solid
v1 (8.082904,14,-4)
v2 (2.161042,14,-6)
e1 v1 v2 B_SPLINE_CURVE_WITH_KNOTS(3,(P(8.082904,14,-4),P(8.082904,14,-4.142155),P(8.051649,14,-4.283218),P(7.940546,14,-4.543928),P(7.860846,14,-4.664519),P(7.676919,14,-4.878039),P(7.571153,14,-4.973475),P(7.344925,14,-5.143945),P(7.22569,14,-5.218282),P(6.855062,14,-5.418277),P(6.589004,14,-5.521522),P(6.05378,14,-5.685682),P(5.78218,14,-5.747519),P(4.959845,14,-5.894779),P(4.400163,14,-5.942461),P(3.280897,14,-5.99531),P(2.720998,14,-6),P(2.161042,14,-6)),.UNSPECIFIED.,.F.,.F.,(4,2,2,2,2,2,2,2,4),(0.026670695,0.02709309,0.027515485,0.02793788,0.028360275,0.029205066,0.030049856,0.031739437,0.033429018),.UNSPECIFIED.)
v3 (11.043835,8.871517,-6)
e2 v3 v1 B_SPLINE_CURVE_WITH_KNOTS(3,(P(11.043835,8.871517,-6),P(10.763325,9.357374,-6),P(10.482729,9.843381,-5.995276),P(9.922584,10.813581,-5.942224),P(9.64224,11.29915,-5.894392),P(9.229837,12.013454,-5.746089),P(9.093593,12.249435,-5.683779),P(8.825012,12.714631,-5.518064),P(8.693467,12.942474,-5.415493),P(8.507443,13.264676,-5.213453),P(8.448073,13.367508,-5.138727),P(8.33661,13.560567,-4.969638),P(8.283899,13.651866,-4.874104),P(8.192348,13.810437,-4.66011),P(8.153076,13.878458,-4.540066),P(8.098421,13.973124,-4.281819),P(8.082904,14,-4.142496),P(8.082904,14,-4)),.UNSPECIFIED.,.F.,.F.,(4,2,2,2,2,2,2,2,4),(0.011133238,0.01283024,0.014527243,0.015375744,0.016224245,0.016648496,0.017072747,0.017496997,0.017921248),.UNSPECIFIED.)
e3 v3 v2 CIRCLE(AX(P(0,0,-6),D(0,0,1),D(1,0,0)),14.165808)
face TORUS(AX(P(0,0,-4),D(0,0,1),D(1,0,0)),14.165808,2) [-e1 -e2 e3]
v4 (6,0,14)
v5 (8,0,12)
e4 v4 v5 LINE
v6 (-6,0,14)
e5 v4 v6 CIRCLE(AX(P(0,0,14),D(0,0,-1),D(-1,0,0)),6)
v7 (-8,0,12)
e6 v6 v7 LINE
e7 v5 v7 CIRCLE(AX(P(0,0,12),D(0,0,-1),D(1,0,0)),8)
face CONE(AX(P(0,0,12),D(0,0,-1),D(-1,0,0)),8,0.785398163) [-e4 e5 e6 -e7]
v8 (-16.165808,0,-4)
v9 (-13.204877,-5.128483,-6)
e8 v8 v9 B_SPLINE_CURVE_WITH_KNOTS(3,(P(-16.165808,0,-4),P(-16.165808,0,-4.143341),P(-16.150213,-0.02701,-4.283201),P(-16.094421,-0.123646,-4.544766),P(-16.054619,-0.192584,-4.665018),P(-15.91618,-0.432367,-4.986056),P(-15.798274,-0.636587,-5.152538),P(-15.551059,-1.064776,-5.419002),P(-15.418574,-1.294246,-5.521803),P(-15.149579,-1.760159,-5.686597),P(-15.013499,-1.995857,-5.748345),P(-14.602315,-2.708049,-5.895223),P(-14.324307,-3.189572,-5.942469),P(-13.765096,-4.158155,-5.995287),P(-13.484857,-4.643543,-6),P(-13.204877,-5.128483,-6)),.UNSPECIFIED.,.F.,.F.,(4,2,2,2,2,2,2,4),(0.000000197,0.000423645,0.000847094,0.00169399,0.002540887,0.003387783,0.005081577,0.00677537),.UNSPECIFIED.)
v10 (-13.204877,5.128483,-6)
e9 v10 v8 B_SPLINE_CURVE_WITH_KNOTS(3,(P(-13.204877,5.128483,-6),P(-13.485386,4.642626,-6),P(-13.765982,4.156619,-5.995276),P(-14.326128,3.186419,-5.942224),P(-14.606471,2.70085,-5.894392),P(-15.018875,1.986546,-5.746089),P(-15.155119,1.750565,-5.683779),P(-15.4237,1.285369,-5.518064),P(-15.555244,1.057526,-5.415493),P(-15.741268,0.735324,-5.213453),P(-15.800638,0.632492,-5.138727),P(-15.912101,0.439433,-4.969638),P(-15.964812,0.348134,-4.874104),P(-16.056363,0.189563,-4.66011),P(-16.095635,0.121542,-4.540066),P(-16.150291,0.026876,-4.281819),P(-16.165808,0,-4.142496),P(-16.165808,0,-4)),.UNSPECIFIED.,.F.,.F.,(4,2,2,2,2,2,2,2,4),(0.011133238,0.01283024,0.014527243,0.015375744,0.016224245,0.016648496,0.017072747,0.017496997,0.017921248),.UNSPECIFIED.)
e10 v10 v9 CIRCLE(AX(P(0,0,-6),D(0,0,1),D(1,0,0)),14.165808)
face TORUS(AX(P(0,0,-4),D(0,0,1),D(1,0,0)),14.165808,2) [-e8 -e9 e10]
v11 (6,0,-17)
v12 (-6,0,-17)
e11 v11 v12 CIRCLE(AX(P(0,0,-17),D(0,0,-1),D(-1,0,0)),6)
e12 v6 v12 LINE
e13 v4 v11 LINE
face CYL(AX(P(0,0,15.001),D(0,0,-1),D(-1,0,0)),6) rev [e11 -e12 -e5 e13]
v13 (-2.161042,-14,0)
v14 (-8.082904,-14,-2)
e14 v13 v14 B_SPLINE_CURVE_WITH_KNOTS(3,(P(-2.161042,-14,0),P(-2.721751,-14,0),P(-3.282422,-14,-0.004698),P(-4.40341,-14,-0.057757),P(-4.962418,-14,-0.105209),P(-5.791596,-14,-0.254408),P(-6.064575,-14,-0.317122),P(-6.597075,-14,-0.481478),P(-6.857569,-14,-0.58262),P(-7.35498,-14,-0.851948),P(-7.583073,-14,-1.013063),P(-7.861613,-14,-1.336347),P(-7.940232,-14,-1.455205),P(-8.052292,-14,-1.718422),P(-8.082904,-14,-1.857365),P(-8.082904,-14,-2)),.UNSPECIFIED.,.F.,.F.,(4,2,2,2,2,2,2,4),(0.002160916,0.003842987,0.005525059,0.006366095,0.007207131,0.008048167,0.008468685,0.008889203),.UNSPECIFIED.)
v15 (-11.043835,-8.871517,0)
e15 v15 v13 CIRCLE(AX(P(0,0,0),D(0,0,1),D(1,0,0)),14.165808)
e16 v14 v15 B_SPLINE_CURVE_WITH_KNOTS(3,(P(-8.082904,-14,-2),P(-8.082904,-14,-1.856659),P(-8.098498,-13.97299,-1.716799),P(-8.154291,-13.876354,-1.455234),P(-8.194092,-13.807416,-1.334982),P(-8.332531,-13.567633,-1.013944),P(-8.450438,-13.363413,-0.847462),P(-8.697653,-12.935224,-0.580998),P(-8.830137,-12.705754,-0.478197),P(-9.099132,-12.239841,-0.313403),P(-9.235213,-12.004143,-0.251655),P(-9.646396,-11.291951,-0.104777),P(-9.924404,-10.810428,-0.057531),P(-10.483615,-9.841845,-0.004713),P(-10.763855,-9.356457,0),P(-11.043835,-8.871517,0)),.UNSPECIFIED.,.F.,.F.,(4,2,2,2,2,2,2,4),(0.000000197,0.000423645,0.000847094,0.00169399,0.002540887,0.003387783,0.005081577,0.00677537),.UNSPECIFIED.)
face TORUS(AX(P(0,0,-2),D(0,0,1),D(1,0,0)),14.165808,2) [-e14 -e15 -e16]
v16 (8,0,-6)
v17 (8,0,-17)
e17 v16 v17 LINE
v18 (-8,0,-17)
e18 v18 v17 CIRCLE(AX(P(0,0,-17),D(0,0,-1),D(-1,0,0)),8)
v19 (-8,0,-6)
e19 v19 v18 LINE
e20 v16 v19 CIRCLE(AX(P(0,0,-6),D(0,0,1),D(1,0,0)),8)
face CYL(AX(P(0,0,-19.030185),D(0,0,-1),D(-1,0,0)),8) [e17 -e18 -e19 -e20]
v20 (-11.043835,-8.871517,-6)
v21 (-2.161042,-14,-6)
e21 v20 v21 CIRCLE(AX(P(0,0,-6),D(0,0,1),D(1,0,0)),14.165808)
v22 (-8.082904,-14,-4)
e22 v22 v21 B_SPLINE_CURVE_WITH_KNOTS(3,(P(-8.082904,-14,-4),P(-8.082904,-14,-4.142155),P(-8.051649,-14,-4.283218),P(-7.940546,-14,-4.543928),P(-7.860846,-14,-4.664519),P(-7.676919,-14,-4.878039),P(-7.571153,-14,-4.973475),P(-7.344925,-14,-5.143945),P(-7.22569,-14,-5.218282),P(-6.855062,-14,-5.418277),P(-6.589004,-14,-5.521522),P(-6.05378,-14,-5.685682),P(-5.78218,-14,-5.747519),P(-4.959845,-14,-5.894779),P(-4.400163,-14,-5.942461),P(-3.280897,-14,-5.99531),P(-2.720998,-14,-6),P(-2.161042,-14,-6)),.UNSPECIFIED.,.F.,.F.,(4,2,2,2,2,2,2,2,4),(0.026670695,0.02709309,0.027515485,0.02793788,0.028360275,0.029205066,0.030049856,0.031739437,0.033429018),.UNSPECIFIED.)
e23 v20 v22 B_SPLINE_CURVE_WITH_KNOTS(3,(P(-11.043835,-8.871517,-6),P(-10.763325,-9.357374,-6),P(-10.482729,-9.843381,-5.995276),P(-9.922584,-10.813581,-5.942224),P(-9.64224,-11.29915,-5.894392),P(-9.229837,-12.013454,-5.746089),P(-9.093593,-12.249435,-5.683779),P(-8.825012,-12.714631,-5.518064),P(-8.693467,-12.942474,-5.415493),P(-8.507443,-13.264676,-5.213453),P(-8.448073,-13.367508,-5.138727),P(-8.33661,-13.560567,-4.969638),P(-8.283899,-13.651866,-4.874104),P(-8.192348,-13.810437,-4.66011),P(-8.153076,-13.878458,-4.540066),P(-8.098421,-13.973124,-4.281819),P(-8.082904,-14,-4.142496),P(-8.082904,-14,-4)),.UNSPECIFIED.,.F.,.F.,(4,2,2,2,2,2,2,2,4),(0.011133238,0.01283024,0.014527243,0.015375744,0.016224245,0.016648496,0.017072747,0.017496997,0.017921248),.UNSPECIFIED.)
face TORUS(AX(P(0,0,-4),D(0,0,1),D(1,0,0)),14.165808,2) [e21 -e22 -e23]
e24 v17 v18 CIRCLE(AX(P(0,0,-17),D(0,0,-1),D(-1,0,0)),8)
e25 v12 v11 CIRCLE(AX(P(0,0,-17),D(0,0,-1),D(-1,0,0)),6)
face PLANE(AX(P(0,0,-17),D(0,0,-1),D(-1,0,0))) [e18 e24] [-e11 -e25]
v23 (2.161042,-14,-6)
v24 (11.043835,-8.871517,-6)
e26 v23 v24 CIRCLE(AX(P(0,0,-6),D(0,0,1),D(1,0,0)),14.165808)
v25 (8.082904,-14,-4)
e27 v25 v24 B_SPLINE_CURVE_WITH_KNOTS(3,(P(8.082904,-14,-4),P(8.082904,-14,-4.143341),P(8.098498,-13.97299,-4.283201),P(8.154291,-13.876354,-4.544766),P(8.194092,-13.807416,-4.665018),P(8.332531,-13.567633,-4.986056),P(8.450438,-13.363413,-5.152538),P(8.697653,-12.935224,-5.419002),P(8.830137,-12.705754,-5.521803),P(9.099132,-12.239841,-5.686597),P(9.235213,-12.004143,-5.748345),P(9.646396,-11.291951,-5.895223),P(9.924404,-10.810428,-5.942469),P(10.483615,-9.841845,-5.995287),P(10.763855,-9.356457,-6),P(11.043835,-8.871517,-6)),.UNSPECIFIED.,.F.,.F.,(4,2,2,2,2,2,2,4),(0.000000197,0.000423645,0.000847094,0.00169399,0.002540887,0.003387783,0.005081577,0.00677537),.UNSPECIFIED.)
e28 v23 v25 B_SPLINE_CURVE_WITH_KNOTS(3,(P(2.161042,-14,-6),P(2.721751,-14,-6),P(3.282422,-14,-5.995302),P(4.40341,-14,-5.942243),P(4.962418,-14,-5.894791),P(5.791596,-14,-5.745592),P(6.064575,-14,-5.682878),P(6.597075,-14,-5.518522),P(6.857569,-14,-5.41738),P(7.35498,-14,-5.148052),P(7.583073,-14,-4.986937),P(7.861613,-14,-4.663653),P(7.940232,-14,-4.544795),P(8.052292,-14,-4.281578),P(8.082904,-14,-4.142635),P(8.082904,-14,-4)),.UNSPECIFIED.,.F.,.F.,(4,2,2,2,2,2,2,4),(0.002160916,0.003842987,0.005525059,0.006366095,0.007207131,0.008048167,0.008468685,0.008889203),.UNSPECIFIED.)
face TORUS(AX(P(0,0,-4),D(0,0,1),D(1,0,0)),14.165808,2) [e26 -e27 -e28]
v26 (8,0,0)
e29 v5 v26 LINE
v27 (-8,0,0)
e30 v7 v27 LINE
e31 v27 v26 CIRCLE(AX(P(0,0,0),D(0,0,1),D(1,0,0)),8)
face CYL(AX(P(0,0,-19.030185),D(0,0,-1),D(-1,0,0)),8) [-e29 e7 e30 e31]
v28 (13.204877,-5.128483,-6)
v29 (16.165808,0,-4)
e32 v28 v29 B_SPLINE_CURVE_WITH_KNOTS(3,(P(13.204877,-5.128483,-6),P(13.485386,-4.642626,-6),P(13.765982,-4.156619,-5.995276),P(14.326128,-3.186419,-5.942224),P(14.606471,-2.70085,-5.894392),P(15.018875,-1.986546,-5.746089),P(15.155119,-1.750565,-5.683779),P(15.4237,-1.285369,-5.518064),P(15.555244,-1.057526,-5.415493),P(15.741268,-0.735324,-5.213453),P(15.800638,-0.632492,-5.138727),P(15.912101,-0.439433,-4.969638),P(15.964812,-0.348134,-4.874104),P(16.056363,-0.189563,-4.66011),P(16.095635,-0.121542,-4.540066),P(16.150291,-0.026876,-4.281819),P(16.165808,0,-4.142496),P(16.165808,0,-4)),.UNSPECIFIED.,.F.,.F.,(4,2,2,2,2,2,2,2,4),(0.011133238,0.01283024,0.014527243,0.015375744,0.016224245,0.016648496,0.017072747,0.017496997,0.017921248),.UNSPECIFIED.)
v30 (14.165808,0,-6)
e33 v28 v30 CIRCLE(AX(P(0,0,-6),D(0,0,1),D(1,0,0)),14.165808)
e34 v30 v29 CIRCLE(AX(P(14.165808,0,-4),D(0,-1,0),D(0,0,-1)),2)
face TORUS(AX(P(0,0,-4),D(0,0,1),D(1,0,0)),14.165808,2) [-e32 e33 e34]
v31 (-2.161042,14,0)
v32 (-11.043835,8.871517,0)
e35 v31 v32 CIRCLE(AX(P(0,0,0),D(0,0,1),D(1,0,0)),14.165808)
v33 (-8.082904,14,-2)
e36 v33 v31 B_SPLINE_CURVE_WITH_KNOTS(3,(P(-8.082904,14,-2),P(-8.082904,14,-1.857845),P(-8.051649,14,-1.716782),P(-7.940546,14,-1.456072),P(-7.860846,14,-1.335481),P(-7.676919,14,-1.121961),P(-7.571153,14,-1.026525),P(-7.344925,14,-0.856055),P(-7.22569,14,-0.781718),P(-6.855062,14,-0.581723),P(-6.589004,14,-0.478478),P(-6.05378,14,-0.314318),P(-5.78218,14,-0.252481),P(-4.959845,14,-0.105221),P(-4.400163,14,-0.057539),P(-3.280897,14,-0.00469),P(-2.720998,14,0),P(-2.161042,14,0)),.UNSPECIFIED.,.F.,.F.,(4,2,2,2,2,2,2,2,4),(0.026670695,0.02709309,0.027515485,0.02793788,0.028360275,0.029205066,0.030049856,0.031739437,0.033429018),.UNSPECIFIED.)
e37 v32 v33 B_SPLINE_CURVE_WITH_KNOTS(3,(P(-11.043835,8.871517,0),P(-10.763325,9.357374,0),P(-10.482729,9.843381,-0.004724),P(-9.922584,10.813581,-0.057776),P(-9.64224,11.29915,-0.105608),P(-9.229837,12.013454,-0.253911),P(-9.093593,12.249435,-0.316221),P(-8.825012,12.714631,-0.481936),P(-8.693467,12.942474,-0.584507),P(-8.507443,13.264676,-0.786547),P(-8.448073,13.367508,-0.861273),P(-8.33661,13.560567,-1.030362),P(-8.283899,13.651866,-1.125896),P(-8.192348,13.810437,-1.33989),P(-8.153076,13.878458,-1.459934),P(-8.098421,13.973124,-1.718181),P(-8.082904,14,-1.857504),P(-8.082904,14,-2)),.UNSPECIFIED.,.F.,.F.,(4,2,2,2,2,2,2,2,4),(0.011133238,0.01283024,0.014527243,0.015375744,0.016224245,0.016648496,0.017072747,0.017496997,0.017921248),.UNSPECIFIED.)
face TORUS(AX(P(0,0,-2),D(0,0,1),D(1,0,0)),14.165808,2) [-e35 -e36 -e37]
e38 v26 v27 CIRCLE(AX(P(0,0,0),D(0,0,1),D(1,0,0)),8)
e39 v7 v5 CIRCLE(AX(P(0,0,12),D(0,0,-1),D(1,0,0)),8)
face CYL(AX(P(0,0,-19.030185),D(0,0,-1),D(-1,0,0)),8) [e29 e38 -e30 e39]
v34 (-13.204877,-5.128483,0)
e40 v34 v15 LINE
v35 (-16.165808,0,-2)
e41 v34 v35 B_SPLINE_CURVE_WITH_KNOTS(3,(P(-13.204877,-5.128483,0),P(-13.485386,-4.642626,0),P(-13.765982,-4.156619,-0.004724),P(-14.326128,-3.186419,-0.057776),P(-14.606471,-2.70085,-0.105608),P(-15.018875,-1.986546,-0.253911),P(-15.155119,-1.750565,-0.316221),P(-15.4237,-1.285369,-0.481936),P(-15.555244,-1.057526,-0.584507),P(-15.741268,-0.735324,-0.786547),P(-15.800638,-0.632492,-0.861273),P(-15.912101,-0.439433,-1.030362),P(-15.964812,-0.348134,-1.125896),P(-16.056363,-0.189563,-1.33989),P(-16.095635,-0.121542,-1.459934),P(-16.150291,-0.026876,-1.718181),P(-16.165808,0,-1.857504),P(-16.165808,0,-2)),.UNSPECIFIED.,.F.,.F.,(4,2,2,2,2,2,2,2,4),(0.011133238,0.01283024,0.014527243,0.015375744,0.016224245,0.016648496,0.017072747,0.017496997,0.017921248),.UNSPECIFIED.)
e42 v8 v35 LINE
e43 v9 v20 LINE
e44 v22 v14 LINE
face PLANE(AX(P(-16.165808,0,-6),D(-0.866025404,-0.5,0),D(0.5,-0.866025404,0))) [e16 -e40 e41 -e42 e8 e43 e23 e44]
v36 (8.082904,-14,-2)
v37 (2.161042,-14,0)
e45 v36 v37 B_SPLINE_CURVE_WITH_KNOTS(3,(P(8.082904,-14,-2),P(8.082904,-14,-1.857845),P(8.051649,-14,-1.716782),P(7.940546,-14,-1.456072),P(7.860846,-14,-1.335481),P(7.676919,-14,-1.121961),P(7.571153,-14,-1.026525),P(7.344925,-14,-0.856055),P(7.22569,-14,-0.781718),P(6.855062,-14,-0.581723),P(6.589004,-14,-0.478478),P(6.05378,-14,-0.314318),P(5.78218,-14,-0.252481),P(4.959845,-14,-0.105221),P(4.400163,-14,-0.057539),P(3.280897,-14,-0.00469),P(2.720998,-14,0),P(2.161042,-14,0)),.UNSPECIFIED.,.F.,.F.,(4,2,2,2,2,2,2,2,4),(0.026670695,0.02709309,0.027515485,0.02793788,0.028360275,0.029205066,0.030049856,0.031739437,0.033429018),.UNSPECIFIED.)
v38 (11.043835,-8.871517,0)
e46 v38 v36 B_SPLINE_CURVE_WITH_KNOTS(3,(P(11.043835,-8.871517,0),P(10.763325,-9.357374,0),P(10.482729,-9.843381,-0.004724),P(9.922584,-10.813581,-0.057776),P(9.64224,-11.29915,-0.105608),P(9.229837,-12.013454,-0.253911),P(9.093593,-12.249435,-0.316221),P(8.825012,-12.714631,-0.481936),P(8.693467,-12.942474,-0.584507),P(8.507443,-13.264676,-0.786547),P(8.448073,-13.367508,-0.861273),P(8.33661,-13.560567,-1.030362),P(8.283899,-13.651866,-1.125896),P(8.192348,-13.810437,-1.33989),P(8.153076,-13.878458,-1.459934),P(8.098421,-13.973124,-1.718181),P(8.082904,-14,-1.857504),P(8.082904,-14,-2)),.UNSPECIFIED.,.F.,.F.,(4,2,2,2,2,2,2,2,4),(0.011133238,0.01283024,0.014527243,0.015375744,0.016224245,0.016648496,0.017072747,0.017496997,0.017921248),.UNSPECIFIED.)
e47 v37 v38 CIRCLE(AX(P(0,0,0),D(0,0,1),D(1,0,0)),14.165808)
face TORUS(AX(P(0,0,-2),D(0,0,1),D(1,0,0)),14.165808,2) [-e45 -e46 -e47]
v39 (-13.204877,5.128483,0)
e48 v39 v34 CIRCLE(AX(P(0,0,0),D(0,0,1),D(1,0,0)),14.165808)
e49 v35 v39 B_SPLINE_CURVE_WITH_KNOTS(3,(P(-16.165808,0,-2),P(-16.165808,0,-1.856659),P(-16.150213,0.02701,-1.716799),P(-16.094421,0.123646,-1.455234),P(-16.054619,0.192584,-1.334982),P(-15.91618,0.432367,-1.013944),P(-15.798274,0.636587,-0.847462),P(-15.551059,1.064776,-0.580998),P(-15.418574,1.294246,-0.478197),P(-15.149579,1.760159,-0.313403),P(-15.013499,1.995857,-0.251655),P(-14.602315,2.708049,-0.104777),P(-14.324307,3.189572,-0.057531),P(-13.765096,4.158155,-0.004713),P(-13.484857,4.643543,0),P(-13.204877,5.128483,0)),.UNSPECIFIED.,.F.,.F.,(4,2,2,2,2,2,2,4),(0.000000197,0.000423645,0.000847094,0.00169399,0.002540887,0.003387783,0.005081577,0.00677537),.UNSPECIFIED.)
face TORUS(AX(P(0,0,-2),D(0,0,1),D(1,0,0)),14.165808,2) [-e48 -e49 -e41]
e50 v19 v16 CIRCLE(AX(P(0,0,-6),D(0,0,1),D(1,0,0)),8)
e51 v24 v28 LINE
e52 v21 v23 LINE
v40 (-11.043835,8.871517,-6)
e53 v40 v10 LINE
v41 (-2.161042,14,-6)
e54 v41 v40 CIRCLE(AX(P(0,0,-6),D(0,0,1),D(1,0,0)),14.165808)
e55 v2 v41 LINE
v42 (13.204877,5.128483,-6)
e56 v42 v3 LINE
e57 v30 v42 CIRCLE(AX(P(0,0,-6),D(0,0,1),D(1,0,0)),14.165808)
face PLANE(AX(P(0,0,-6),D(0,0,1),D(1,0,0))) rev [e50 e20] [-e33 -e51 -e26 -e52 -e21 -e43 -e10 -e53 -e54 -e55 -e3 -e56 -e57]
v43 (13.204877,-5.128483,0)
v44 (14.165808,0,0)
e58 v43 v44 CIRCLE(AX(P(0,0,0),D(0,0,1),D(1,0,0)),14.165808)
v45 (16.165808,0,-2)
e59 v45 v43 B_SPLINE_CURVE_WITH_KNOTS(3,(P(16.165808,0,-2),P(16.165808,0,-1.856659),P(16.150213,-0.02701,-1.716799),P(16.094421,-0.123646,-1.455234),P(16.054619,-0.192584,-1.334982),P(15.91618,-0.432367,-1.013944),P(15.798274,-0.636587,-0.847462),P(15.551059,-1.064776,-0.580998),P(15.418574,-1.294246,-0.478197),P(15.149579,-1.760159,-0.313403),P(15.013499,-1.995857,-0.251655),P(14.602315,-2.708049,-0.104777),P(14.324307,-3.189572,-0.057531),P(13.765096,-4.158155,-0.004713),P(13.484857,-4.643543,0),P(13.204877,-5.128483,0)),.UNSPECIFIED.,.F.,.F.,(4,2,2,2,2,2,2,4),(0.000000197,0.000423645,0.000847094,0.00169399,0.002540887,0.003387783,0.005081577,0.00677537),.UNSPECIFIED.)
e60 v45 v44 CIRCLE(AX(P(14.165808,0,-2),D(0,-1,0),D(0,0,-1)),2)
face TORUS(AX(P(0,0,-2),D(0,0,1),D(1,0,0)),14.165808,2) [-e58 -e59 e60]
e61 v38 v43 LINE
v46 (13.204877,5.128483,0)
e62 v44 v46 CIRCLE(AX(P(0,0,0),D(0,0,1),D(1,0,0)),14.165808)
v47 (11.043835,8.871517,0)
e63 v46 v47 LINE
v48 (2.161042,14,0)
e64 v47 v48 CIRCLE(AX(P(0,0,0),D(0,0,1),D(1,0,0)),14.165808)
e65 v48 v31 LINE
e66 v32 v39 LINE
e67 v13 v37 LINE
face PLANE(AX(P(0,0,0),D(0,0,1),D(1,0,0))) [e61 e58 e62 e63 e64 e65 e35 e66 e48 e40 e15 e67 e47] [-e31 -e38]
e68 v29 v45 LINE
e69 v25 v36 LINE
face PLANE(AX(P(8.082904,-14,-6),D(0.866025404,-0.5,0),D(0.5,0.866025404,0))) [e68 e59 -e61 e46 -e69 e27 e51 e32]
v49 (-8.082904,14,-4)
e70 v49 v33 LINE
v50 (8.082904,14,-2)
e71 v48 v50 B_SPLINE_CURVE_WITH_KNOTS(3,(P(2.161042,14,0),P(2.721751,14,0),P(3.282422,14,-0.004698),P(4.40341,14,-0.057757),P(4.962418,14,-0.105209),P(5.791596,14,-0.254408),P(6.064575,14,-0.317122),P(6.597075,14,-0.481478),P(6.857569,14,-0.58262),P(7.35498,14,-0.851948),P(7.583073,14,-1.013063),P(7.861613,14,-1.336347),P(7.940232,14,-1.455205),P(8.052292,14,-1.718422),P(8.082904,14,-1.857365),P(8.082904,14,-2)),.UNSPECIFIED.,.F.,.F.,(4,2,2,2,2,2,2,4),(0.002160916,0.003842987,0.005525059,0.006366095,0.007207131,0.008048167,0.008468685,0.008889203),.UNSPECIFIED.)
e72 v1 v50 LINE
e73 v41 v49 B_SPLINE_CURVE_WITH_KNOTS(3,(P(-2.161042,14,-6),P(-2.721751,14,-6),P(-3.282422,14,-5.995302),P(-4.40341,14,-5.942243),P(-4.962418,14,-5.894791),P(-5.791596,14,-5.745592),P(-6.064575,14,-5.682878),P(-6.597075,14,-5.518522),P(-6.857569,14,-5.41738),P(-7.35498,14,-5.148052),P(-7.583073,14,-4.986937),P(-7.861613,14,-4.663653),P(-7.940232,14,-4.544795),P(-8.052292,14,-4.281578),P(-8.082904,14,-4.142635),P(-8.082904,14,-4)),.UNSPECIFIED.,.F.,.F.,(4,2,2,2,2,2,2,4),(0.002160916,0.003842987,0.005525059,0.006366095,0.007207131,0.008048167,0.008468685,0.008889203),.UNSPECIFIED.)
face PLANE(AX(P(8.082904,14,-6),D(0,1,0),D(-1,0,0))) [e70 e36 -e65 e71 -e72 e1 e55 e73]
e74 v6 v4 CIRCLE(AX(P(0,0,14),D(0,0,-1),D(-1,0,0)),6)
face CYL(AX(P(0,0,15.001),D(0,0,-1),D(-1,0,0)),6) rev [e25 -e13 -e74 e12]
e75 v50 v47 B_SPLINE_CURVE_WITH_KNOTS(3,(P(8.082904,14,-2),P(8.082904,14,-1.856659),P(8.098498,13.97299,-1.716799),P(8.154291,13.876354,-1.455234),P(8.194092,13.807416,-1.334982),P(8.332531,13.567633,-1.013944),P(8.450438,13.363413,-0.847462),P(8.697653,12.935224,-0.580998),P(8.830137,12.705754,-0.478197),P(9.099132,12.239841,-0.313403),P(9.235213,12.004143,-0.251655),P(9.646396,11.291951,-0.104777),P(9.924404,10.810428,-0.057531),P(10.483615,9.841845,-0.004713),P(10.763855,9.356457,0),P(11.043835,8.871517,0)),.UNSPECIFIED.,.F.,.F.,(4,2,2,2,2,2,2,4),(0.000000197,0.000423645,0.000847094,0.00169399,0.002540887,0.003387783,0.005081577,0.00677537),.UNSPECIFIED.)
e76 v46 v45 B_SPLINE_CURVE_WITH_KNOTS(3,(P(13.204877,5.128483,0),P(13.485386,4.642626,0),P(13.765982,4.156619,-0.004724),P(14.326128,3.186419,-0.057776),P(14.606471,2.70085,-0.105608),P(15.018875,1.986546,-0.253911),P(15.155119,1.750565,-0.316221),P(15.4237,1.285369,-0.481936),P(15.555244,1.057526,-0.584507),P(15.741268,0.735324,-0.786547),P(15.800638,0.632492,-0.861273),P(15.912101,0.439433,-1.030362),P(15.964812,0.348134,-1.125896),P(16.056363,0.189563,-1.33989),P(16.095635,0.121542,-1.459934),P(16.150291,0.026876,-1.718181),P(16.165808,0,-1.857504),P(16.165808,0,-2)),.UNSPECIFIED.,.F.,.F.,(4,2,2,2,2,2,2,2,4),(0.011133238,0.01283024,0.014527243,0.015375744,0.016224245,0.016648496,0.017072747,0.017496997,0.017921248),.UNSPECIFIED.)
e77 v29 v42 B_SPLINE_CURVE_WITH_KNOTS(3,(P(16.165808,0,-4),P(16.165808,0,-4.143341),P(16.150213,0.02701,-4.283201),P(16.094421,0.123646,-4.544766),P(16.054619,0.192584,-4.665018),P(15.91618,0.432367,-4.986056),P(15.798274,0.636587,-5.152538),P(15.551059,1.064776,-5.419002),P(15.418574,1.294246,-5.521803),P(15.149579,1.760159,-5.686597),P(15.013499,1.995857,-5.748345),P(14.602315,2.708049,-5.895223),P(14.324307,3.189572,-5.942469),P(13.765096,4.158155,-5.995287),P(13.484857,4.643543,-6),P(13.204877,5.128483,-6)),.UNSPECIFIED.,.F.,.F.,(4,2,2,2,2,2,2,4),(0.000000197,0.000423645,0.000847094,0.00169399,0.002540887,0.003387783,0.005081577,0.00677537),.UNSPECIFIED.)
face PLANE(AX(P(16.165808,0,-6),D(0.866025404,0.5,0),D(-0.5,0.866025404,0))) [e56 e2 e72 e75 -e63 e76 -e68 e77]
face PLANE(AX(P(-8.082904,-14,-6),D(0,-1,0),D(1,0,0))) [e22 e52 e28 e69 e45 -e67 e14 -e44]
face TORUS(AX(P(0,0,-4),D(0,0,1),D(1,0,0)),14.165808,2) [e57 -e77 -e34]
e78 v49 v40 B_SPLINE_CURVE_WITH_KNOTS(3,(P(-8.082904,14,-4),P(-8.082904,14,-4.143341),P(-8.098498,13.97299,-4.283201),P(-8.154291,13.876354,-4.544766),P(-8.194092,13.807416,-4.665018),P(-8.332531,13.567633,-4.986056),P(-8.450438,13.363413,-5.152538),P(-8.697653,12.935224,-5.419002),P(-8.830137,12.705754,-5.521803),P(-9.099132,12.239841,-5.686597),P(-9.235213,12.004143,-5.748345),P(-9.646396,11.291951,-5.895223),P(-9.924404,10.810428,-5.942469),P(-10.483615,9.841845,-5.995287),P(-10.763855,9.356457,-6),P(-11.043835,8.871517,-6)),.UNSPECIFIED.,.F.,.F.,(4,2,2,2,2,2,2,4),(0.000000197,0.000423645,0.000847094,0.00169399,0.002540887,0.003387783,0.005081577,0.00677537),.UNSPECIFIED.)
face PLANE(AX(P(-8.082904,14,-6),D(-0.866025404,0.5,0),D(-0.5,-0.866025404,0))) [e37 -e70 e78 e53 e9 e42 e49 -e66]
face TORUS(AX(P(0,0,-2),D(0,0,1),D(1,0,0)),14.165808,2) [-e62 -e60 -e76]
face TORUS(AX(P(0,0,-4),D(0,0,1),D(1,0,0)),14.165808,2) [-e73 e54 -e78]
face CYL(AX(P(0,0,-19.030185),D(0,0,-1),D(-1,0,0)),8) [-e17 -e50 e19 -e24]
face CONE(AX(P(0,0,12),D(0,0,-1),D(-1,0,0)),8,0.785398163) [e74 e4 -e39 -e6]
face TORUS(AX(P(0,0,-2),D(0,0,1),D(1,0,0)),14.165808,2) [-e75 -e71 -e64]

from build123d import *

# Parameters (mm, degrees)
HEX_BODY_28_DEPTH        = 6
SPIGOT_CHAMFER_3X45_SIZE = 3
THROUGH_BORE_10_REACH    = 40.488
BORE_SKETCH_10_R         = 6


with BuildPart() as part:
    # Hex Profile Sketch → Hex Body 28 (new body)
    with BuildSketch(Plane.XY):
        Polygon((8.082903769, 14), (-8.082903769, 14), (-16.165807537, 0), (-8.082903769, -14), (8.082903769, -14), (16.165807537, 0), align=None)
    extrude(amount=-HEX_BODY_28_DEPTH)

    # Spigot Profile Sketch → Threaded Spigots (revolve)
    with BuildSketch(Plane(origin=(0, 0, 0), x_dir=(1, 0, 0), z_dir=(0, 1, 0))):
        Polygon((0, 17), (-8, 17), (-8, -7), (-8, -15), (0, -15), align=None)
    revolve(axis=Axis((0, 0, -19.030185158), (0, 0, 1)))

    # Spigot Chamfer 3x45
    spigot_chamfer_3x45_edges = [part.edges().sort_by_distance(p)[0] for p in [
        (8, 0, 15),
    ]]
    chamfer(spigot_chamfer_3x45_edges, length=SPIGOT_CHAMFER_3X45_SIZE)

    # Through Bore Ø10: up to this cone (the profile starts inside it)
    through_bore_10_end = Plane(origin=(0, 0, -17), z_dir=(0, 0, -1)).offset(-36.999999) * Cone(1e-06, 114.988, 114.987999, align=(Align.CENTER, Align.CENTER, Align.MIN), mode=Mode.PRIVATE)
    # Bore Sketch Ø10 → Through Bore Ø10 (cut, up to the surface)
    with BuildSketch(Plane(origin=(0, 0, -17), x_dir=(-1, 0, 0), z_dir=(0, 0, -1)), mode=Mode.PRIVATE) as through_bore_10_sk1:
        Circle(BORE_SKETCH_10_R)
    through_bore_10_tool1 = extrude(through_bore_10_sk1.sketch, amount=-THROUGH_BORE_10_REACH, mode=Mode.PRIVATE) & through_bore_10_end
    add(through_bore_10_tool1.solids().sort_by_distance((0, 0, -17))[0], mode=Mode.SUBTRACT)

    # Thread Groove Profile Sketch → Thread Grooves (revolve, cut)
    with BuildSketch(Plane(origin=(0, 0, 0), x_dir=(1, 0, 0), z_dir=(0, 1, 0))):
        with BuildLine():
            Line((-14.165807537, 6), (-16.165807537, 6))
            Line((-16.165807537, 6), (-16.165807537, 4))
            ThreePointArc((-16.165807537, 4), (-15.5800211, 5.414213562), (-14.165807537, 6))
        make_face()
        with BuildLine():
            Line((-16.165807537, 0), (-16.165807537, 2))
            ThreePointArc((-16.165807537, 2), (-15.5800211, 0.585786438), (-14.165807537, 0))
            Line((-14.165807537, 0), (-16.165807537, 0))
        make_face()
    revolve(axis=Axis((0, 0, 0), (0, 0, -1)), mode=Mode.SUBTRACT)


solid = part.part
